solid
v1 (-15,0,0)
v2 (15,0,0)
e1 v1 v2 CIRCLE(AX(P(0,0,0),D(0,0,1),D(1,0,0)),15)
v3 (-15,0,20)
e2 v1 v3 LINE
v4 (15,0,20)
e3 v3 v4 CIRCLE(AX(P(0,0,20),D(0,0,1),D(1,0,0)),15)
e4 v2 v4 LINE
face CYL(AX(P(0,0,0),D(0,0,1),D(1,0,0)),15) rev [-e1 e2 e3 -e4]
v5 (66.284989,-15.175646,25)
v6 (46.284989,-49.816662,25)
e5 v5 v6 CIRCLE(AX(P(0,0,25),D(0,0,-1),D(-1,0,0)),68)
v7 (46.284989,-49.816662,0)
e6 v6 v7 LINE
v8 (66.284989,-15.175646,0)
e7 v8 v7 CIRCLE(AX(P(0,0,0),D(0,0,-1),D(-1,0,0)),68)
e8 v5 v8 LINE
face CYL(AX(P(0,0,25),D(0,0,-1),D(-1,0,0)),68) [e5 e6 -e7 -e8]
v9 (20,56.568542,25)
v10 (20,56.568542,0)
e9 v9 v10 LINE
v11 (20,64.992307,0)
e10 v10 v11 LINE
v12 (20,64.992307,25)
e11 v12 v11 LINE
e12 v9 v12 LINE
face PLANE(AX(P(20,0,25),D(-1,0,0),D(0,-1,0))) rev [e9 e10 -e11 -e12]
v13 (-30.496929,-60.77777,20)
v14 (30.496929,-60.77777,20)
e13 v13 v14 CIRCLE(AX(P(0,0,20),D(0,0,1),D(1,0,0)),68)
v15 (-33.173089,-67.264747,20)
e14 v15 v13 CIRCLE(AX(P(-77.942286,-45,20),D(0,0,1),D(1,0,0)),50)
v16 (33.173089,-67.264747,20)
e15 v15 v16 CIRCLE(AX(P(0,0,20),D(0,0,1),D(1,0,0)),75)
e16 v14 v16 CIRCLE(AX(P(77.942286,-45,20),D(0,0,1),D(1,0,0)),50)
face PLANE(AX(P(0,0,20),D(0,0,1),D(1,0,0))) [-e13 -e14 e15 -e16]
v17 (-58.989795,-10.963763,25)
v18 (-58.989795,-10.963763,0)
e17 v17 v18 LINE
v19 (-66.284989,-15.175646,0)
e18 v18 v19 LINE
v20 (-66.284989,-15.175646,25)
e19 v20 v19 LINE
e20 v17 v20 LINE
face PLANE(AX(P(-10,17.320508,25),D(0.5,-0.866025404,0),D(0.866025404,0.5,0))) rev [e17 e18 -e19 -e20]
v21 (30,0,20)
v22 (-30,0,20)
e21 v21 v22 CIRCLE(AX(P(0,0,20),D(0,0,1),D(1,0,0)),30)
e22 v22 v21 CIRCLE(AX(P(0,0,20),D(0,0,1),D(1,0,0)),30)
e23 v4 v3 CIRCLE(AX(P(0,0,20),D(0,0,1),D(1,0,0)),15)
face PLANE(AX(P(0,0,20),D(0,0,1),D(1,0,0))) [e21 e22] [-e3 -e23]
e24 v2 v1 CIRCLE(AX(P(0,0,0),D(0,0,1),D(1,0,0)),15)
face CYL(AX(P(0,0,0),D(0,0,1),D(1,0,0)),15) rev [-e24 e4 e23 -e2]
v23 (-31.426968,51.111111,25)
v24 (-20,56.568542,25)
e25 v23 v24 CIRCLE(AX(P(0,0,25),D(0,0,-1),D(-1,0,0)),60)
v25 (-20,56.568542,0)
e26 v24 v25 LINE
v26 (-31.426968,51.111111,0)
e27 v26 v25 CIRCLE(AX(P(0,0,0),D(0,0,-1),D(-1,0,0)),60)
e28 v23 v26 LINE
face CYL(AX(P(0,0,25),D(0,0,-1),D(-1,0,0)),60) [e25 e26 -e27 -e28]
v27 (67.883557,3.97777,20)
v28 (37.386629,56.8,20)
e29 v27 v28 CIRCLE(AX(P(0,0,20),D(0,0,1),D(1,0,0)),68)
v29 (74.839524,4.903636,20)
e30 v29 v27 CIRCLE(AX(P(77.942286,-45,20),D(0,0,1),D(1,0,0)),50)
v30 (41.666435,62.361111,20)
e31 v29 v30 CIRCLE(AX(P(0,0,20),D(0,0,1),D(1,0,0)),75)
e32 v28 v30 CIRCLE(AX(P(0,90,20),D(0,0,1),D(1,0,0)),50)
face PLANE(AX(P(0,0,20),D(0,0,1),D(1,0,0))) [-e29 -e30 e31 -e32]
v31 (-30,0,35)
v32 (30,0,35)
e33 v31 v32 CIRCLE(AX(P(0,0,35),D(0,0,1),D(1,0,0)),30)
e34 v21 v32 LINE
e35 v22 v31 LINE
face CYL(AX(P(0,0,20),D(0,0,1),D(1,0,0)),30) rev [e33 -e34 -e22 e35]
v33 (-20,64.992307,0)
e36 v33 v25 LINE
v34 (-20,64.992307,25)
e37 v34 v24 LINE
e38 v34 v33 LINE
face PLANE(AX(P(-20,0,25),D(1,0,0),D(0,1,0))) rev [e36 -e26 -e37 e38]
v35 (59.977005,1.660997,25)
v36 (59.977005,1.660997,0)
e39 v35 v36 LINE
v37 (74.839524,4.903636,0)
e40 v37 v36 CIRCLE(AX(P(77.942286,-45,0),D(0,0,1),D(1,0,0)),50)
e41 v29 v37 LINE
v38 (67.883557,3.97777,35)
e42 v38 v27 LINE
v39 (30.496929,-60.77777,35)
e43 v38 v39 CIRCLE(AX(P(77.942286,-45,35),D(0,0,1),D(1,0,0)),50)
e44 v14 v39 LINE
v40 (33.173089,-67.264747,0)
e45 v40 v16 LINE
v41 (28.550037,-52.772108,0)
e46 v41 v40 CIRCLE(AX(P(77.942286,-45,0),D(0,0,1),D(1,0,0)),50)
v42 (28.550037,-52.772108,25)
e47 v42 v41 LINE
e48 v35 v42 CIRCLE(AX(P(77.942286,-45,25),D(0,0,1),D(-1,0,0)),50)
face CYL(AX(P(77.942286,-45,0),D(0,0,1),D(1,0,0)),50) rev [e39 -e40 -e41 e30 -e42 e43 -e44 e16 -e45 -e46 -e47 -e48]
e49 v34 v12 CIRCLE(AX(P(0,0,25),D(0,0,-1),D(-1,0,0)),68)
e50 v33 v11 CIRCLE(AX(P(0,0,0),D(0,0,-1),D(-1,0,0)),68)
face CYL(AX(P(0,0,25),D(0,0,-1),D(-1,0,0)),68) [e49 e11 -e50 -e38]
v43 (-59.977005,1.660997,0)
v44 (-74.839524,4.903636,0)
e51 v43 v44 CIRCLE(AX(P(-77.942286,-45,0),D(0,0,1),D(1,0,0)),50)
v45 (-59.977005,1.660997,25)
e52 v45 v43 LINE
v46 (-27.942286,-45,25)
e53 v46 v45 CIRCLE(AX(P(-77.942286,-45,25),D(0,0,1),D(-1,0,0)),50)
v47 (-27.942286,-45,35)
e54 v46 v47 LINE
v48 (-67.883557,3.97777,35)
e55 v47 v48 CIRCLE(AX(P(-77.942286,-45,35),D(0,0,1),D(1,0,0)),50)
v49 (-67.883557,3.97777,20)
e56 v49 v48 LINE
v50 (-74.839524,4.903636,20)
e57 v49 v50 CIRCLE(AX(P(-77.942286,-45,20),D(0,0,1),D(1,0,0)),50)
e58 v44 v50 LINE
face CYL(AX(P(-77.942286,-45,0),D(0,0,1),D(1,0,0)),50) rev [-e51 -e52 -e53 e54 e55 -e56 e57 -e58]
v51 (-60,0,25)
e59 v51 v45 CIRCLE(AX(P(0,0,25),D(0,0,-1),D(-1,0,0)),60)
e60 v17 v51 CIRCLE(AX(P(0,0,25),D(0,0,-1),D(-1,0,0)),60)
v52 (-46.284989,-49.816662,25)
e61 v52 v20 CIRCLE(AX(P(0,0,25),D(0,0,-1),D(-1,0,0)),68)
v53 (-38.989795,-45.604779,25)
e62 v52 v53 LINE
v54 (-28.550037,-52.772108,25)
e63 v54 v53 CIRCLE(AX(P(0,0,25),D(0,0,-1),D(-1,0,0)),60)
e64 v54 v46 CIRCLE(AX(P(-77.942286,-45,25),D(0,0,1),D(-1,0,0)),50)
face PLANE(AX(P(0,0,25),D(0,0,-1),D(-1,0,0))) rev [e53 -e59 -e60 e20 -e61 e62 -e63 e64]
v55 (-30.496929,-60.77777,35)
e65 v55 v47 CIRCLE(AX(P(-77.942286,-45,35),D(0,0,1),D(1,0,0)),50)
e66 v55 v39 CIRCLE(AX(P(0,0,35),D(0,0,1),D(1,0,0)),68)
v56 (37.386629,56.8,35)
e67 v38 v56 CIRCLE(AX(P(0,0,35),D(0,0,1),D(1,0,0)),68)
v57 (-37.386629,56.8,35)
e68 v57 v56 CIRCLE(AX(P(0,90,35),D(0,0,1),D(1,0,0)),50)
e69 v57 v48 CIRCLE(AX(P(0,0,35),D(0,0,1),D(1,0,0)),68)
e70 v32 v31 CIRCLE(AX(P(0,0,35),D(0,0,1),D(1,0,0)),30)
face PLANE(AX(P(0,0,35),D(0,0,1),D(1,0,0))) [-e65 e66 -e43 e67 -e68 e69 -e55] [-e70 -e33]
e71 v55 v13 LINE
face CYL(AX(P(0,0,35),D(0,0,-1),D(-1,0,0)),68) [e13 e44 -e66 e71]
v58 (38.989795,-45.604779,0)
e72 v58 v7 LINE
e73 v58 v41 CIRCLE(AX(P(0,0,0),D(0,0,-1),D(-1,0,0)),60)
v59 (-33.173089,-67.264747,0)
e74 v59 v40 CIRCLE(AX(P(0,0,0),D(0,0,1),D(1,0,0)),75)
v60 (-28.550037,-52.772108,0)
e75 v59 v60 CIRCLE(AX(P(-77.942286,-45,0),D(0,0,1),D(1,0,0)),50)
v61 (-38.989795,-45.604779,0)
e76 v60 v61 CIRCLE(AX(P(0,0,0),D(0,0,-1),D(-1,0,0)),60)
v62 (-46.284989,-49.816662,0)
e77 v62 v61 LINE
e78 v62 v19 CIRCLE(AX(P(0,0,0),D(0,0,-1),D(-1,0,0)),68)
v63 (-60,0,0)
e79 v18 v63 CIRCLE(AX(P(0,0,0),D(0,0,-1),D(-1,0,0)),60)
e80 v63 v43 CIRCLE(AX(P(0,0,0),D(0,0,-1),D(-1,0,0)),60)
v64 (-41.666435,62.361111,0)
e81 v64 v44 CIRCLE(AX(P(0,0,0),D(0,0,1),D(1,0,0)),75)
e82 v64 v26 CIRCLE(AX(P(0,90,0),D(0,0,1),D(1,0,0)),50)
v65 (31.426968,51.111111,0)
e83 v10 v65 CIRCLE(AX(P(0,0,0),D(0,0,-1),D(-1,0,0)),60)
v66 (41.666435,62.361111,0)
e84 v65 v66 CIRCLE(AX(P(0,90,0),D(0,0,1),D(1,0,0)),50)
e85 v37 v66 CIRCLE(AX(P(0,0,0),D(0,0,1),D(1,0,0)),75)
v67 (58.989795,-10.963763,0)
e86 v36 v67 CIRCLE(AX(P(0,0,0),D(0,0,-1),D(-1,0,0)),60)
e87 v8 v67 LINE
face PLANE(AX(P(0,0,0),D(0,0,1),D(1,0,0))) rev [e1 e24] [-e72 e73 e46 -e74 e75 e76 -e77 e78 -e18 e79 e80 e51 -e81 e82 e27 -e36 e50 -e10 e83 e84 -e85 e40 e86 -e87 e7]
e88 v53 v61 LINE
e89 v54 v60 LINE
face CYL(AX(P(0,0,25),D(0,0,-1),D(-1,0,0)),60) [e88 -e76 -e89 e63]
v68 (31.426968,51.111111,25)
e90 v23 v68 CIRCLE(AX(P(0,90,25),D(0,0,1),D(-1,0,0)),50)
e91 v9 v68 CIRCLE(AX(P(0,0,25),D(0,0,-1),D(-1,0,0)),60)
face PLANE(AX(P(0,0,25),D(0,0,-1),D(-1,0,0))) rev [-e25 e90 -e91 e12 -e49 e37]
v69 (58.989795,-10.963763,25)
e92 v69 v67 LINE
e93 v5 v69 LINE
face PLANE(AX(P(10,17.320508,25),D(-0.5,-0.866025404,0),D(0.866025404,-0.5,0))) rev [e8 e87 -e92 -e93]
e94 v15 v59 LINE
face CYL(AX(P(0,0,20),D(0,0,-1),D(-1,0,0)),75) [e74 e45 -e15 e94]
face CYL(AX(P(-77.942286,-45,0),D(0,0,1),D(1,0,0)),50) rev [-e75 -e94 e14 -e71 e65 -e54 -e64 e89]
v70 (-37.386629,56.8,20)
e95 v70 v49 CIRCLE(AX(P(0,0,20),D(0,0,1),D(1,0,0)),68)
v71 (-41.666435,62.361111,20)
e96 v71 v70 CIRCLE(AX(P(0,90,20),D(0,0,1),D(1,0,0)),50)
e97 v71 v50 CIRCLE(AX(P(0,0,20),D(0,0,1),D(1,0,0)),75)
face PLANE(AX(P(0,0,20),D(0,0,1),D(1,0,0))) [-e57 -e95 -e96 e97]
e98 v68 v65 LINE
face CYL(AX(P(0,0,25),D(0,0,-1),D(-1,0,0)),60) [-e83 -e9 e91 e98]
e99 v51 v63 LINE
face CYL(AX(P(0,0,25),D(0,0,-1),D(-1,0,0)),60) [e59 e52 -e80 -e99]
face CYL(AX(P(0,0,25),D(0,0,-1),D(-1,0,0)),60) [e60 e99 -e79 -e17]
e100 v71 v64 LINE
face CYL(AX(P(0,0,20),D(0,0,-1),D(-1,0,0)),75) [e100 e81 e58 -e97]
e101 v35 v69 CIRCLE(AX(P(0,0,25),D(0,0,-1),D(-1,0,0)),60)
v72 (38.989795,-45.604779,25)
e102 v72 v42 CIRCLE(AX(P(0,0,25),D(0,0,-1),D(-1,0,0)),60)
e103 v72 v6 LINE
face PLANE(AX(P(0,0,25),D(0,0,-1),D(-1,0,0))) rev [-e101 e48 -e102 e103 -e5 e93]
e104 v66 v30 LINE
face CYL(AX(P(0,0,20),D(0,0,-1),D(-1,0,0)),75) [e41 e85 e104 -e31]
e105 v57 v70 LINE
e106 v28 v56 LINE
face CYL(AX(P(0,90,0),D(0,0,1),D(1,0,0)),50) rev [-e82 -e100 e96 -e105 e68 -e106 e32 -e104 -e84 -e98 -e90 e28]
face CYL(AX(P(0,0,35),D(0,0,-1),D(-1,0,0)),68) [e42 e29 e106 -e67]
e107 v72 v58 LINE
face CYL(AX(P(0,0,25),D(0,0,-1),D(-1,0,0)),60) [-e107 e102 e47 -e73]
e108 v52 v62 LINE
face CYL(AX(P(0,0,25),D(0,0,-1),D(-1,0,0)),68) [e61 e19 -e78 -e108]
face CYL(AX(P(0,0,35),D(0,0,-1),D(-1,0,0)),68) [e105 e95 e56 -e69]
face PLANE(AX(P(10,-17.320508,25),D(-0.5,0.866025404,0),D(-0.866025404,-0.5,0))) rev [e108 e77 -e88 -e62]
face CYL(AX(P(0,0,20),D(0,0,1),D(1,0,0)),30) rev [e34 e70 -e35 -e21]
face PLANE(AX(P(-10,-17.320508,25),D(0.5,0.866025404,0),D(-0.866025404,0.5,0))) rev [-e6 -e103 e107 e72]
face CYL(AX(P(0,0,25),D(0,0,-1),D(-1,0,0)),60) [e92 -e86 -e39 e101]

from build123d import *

# Parameters (mm, degrees)
BASE_DISC_SKETCH_R    = 75
BASE_DISC_DEPTH       = 20
HUB_BOSS_SKETCH_R     = 68
HUB_BOSS_DEPTH        = 15
LOBE_START            = -35
LOBE_RECESS_CUT_DEPTH = 35
COUPLING_LOBES_DEPTH  = 25
COUNTERBORE_SKETCH_R  = 30
COUNTERBORE_DEPTH     = 15
THROUGH_BORE_SKETCH_R = 15
THROUGH_BORE_DEPTH    = 20


with BuildPart() as part:
    # Base Disc Sketch → Base Disc (new body)
    with BuildSketch(Plane.XY):
        Circle(BASE_DISC_SKETCH_R)
    extrude(amount=BASE_DISC_DEPTH)

    # Hub Boss Sketch → Hub Boss (add)
    with BuildSketch(Plane.XY.offset(20)):
        Circle(HUB_BOSS_SKETCH_R)
    extrude(amount=HUB_BOSS_DEPTH)

    # Lobe Recess Sketch → Lobe Recess Cut (cut)
    with BuildSketch(Plane.XY.offset(35).offset(LOBE_START)):
        with BuildLine():
            ThreePointArc((-37.386628626, 56.8), (-19.514097468, 65.139849555), (0, 68))
            Line((0, 68), (0, 90))
            ThreePointArc((0, 90), (-25, 86.458082329), (-48.032267961, 76.111111111))
            ThreePointArc((-48.032267961, 76.111111111), (-43.787289555, 65.861373829), (-37.386628626, 56.8))
        make_face()
        with BuildLine():
            Line((0, 90), (0, 68))
            ThreePointArc((0, 68), (19.514097468, 65.139849555), (37.386628626, 56.8))
            ThreePointArc((37.386628626, 56.8), (43.787289555, 65.861373829), (48.032267961, 76.111111111))
            ThreePointArc((48.032267961, 76.111111111), (25, 86.458082329), (0, 90))
        make_face()
        with BuildLine():
            ThreePointArc((-37.386628626, 56.8), (-20.493901532, 44.392982996), (0, 40))
            Line((0, 40), (0, 68))
            ThreePointArc((0, 68), (-19.514097468, 65.139849555), (-37.386628626, 56.8))
        make_face()
        with BuildLine():
            Line((0, 68), (0, 40))
            ThreePointArc((0, 40), (20.493901532, 44.392982996), (37.386628626, 56.8))
            ThreePointArc((37.386628626, 56.8), (19.514097468, 65.139849555), (0, 68))
        make_face()
        with BuildLine():
            ThreePointArc((58.889727457, -34), (46.655715779, -49.469628917), (30.496928622, -60.777770152))
            ThreePointArc((30.496928622, -60.777770152), (35.143978087, -70.851592032), (41.898021752, -79.652719811))
            ThreePointArc((41.898021752, -79.652719811), (62.374895659, -64.879676259), (77.942286341, -45))
            Line((77.942286341, -45), (58.889727457, -34))
        make_face()
        with BuildLine():
            ThreePointArc((67.883557248, 3.977770152), (67.970883078, 1.989737061), (68, 0))
            ThreePointArc((68, 0), (65.682956188, -17.599695067), (58.889727457, -34))
            Line((58.889727457, -34), (77.942286341, -45))
            ThreePointArc((77.942286341, -45), (86.933324366, -23.293714059), (90, 0))
            ThreePointArc((90, 0), (89.982570741, 1.771147347), (89.930289713, 3.5416087))
            ThreePointArc((89.930289713, 3.5416087), (78.931267642, 4.990218203), (67.883557248, 3.977770152))
        make_face()
        with BuildLine():
            Line((68, 0), (56.147791623, 0))
            ThreePointArc((56.147791623, 0), (43.892842113, -8.385312403), (34.641016151, -20))
            Line((34.641016151, -20), (58.889727457, -34))
            ThreePointArc((58.889727457, -34), (65.682956188, -17.599695067), (68, 0))
        make_face()
        with BuildLine():
            Line((58.889727457, -34), (34.641016151, -20))
            ThreePointArc((34.641016151, -20), (28.198500258, -39.944730847), (30.496928622, -60.777770152))
            ThreePointArc((30.496928622, -60.777770152), (46.655715779, -49.469628917), (58.889727457, -34))
        make_face()
        with BuildLine():
            ThreePointArc((67.883557248, 3.977770152), (61.891970748, 2.353852741), (56.147791623, 0))
            Line((56.147791623, 0), (68, 0))
            ThreePointArc((68, 0), (67.970883078, 1.989737061), (67.883557248, 3.977770152))
        make_face()
        with BuildLine():
            ThreePointArc((-41.898021752, -79.652719811), (-35.143978087, -70.851592032), (-30.496928622, -60.777770152))
            ThreePointArc((-30.496928622, -60.777770152), (-46.655715779, -49.469628917), (-58.889727457, -34))
            Line((-58.889727457, -34), (-77.942286341, -45))
            ThreePointArc((-77.942286341, -45), (-62.374895659, -64.879676259), (-41.898021752, -79.652719811))
        make_face()
        with BuildLine():
            ThreePointArc((-58.889727457, -34), (-65.682956188, -17.599695067), (-68, 0))
            ThreePointArc((-68, 0), (-67.970883078, 1.989737061), (-67.883557248, 3.977770152))
            ThreePointArc((-67.883557248, 3.977770152), (-78.931267642, 4.990218203), (-89.930289713, 3.5416087))
            ThreePointArc((-89.930289713, 3.5416087), (-87.374895659, -21.57840607), (-77.942286341, -45))
            Line((-77.942286341, -45), (-58.889727457, -34))
        make_face()
        with BuildLine():
            ThreePointArc((-34.641016151, -20), (-43.892842113, -8.385312403), (-56.147791623, 0))
            Line((-56.147791623, 0), (-68, 0))
            ThreePointArc((-68, 0), (-65.682956188, -17.599695067), (-58.889727457, -34))
            Line((-58.889727457, -34), (-34.641016151, -20))
        make_face()
        with BuildLine():
            ThreePointArc((-27.942286341, -45), (-29.645995026, -32.059047745), (-34.641016151, -20))
            Line((-34.641016151, -20), (-58.889727457, -34))
            ThreePointArc((-58.889727457, -34), (-46.655715779, -49.469628917), (-30.496928622, -60.777770152))
            ThreePointArc((-30.496928622, -60.777770152), (-28.585078732, -52.99162418), (-27.942286341, -45))
        make_face()
        with BuildLine():
            Line((-68, 0), (-56.147791623, 0))
            ThreePointArc((-56.147791623, 0), (-61.891970748, 2.353852741), (-67.883557248, 3.977770152))
            ThreePointArc((-67.883557248, 3.977770152), (-67.970883078, 1.989737061), (-68, 0))
        make_face()
    extrude(amount=LOBE_RECESS_CUT_DEPTH, mode=Mode.SUBTRACT)

    # Coupling Lobes Sketch → Coupling Lobes (add)
    with BuildSketch(Plane(origin=(0, 0, 0), x_dir=(-1, 0, 0), z_dir=(0, 0, -1))):
        with BuildLine():
            ThreePointArc((-31.426968053, 51.111111111), (-16.666666667, 42.859547921), (0, 40))
            Line((0, 40), (0, 68))
            ThreePointArc((0, 68), (-10.112445497, 67.243872926), (-20, 64.992307237))
            Line((-20, 64.992307237), (-20, 56.568542495))
            ThreePointArc((-20, 56.568542495), (-25.857864376, 54.142135624), (-31.426968053, 51.111111111))
        make_face()
        with BuildLine():
            Line((0, 68), (0, 40))
            ThreePointArc((0, 40), (16.666666667, 42.859547921), (31.426968053, 51.111111111))
            ThreePointArc((31.426968053, 51.111111111), (25.857864376, 54.142135624), (20, 56.568542495))
            Line((20, 56.568542495), (20, 64.992307237))
            ThreePointArc((20, 64.992307237), (10.112445497, 67.243872926), (0, 68))
        make_face()
        with BuildLine():
            Line((-46.284989118, -49.816661694), (-38.989794856, -45.604779323))
            ThreePointArc((-38.989794856, -45.604779323), (-33.959532677, -49.464635249), (-28.550036612, -52.772108253))
            ThreePointArc((-28.550036612, -52.772108253), (-34.641016151, -20), (-59.977004664, 1.660997142))
            ThreePointArc((-59.977004664, 1.660997142), (-59.817397053, -4.677500374), (-58.989794856, -10.963763172))
            Line((-58.989794856, -10.963763172), (-66.284989118, -15.175645543))
            ThreePointArc((-66.284989118, -15.175645543), (-58.889727457, -34), (-46.284989118, -49.816661694))
        make_face()
        with BuildLine():
            Line((66.284989118, -15.175645543), (58.989794856, -10.963763172))
            ThreePointArc((58.989794856, -10.963763172), (59.817397053, -4.677500374), (59.977004664, 1.660997142))
            ThreePointArc((59.977004664, 1.660997142), (34.641016151, -20), (28.550036612, -52.772108253))
            ThreePointArc((28.550036612, -52.772108253), (33.959532677, -49.464635249), (38.989794856, -45.604779323))
            Line((38.989794856, -45.604779323), (46.284989118, -49.816661694))
            ThreePointArc((46.284989118, -49.816661694), (58.889727457, -34), (66.284989118, -15.175645543))
        make_face()
    extrude(amount=-COUPLING_LOBES_DEPTH)

    # Counterbore Sketch → Counterbore (cut)
    with BuildSketch(Plane.XY.offset(35)):
        Circle(COUNTERBORE_SKETCH_R)
    extrude(amount=-COUNTERBORE_DEPTH, mode=Mode.SUBTRACT)

    # Through Bore Sketch → Through Bore (cut)
    with BuildSketch(Plane.XY.offset(20)):
        Circle(THROUGH_BORE_SKETCH_R)
    extrude(amount=-THROUGH_BORE_DEPTH, mode=Mode.SUBTRACT)


solid = part.part
